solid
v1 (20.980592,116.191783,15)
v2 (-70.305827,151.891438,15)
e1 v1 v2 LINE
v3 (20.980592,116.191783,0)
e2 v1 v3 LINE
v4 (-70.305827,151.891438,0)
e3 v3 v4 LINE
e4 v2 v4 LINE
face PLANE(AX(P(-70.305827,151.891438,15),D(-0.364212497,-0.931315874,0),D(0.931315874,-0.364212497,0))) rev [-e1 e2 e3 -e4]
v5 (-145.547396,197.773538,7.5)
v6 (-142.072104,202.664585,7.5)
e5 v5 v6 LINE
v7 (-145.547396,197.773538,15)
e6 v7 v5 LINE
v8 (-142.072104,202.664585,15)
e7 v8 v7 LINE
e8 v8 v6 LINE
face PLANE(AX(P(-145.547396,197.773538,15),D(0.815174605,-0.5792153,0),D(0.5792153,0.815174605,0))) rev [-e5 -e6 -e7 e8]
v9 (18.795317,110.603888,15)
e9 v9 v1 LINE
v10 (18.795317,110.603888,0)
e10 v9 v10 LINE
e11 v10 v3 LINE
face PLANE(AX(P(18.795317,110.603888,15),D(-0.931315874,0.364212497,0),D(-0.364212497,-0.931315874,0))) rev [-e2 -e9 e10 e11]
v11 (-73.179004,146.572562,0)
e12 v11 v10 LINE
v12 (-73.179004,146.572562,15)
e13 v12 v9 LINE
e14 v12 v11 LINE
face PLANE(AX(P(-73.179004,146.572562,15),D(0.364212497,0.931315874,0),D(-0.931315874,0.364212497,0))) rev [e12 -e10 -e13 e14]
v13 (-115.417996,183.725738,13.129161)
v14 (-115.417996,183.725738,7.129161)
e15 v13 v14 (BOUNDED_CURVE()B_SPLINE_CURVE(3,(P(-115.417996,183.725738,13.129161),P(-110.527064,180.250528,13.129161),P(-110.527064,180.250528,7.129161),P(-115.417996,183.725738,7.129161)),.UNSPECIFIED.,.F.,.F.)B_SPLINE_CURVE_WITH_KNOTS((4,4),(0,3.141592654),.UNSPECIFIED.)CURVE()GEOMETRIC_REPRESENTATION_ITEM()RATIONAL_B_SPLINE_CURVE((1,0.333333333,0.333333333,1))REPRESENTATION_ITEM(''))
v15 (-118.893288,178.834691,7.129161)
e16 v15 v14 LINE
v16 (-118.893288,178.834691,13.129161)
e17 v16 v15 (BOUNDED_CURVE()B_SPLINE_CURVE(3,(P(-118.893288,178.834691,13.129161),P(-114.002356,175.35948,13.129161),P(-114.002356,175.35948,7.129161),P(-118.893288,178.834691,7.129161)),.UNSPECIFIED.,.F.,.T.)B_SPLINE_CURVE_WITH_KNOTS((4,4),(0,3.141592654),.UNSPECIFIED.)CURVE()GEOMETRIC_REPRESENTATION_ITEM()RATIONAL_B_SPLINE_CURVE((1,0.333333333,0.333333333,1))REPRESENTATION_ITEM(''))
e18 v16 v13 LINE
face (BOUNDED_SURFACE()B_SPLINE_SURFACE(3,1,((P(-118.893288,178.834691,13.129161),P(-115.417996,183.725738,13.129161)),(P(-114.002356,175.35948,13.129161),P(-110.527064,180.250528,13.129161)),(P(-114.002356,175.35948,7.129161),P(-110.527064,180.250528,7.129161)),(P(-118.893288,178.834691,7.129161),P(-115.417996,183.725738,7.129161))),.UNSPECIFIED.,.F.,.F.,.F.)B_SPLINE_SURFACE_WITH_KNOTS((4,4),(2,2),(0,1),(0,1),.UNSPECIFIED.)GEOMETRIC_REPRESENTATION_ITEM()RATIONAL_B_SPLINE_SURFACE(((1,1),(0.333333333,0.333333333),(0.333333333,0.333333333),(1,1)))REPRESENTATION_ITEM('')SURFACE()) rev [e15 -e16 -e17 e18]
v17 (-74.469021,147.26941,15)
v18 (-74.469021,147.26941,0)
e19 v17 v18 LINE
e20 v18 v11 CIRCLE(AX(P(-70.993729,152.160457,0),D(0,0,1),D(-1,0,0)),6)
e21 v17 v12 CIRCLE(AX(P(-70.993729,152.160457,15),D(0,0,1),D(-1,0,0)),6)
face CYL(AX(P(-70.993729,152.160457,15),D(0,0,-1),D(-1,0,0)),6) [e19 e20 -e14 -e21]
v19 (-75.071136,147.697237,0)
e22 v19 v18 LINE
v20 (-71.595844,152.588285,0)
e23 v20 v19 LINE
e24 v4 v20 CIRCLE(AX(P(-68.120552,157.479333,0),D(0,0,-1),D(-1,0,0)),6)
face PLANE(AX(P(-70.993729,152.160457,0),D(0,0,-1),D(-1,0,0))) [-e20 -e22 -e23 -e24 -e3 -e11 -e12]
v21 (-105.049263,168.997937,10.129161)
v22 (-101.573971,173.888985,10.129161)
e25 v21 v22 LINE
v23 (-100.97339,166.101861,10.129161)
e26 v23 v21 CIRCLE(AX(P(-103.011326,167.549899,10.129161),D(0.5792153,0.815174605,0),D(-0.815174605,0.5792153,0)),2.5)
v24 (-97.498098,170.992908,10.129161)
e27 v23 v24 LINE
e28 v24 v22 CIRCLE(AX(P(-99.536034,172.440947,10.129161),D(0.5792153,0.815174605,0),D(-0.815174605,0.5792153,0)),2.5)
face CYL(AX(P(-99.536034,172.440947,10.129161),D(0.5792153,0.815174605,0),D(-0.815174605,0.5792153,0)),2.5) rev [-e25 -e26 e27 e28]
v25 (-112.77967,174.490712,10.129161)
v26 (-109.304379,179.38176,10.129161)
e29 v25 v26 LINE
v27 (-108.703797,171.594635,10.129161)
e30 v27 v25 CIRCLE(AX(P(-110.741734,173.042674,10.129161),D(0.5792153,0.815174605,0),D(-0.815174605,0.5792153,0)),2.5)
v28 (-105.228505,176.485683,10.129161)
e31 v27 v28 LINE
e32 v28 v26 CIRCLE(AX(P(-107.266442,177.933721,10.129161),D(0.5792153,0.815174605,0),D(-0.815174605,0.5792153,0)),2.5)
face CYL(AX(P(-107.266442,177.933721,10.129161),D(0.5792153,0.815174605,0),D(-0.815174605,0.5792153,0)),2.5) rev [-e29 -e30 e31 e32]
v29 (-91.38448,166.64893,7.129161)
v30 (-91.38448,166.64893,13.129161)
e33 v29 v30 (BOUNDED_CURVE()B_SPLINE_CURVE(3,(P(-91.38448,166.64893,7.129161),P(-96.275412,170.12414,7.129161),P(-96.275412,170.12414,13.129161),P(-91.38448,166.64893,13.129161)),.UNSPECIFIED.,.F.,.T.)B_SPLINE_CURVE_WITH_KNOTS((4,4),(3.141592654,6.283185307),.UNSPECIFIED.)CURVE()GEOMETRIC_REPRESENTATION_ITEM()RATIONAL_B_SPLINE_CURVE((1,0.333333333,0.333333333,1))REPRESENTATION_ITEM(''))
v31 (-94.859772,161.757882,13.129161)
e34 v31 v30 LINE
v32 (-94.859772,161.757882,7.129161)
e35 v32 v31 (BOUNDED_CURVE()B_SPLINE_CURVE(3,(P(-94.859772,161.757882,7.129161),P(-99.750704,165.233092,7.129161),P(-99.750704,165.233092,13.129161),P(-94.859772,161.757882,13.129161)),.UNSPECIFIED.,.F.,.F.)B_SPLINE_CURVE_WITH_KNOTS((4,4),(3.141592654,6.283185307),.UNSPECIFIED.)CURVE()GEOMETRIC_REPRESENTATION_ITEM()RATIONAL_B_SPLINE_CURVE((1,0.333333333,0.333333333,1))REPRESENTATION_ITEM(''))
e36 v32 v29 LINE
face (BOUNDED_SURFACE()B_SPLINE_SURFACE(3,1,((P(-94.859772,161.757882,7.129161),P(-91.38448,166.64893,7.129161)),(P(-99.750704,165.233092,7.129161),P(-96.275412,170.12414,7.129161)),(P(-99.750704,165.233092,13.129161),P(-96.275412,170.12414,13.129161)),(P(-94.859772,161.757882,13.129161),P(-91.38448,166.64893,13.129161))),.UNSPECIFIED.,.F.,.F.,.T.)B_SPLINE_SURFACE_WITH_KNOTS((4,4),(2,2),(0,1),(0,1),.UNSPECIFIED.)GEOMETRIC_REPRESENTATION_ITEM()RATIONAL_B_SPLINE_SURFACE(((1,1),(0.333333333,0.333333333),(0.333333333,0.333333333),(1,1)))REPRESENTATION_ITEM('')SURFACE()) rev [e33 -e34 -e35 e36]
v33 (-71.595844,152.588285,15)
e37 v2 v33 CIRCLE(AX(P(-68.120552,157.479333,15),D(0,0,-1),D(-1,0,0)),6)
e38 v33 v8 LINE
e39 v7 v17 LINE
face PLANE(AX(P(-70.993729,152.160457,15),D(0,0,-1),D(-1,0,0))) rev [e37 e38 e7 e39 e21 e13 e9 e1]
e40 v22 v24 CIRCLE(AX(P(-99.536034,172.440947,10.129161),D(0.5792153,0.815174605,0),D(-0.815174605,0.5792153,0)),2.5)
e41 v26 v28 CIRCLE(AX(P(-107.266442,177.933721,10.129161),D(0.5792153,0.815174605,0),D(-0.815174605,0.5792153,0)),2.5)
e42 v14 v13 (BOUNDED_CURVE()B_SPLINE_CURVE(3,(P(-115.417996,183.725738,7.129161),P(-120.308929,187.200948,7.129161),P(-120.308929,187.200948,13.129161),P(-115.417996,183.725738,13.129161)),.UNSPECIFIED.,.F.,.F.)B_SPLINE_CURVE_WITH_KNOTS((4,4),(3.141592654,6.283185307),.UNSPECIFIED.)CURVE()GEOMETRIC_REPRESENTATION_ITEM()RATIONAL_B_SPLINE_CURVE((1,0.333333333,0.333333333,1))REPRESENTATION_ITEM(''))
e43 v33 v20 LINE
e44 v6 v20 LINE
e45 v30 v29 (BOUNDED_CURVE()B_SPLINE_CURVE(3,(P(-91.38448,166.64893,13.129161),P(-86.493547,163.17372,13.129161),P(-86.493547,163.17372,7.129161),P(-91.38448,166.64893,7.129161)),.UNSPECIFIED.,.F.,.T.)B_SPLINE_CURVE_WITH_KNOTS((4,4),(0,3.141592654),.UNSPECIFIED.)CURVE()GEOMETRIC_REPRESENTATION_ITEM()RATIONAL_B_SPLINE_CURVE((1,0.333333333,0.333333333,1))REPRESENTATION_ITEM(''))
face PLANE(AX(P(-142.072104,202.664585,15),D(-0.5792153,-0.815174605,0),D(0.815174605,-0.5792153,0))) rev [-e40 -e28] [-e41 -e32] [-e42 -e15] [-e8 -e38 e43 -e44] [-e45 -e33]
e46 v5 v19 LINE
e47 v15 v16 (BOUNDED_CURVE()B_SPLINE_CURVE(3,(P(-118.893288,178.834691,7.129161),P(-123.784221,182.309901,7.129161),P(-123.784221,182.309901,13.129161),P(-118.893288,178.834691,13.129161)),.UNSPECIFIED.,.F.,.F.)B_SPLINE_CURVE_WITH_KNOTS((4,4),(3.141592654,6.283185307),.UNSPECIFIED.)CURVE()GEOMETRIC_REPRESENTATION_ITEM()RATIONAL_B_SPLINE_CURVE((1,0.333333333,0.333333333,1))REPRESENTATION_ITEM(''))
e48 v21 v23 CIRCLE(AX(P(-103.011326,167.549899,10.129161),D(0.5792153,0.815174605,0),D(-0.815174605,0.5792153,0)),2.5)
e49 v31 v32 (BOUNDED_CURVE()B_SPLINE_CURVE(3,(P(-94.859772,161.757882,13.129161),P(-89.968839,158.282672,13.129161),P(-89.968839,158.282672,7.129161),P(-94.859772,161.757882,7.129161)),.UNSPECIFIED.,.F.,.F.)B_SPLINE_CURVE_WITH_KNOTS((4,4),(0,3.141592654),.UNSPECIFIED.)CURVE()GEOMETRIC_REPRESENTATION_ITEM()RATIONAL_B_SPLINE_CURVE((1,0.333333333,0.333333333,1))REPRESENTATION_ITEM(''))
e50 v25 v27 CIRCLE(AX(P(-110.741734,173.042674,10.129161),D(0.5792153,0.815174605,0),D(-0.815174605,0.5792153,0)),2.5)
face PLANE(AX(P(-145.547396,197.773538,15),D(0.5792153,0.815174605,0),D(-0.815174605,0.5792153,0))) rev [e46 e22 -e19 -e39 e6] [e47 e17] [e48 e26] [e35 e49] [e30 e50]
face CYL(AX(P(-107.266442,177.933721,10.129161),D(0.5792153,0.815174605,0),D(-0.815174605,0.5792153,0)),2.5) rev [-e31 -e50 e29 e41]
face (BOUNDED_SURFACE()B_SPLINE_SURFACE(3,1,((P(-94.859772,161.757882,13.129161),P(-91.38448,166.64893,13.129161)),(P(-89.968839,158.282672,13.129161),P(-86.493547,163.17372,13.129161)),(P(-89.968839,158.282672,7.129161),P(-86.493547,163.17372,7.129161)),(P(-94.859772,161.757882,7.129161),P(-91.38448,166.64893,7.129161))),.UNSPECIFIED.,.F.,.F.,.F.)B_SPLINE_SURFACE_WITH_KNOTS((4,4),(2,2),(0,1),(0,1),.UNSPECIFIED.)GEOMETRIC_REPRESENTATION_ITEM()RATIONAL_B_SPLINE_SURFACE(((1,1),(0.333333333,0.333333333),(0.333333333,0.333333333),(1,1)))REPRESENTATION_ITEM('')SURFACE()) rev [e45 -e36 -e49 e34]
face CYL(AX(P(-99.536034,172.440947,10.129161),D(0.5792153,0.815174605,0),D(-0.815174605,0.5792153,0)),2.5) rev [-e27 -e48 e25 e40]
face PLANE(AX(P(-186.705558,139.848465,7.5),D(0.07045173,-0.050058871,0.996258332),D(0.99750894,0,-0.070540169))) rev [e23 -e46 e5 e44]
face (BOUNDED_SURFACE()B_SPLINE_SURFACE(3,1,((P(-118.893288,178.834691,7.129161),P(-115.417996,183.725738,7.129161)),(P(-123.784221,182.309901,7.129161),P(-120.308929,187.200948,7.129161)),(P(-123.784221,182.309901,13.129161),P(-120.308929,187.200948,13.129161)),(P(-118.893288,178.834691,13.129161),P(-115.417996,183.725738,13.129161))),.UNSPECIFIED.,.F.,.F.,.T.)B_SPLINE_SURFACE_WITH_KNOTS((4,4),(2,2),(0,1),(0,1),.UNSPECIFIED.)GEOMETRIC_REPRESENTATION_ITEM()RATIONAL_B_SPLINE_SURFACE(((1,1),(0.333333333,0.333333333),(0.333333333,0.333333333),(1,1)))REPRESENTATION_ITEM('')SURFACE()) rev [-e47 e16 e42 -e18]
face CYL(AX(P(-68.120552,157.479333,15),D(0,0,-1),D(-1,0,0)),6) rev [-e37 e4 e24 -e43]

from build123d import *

# Parameters (mm, degrees)
EXTRUDE_1_DEPTH     = 15
CUT_EXTRUDE_1_DEPTH = 237.517683659
SKETCH_5_RX         = 3
SKETCH_5_RY         = 2.999929495
CUT_EXTRUDE_2_DEPTH = 237.517683659
HOLE_WIZARD_M6_1_D  = 5


with BuildPart() as part:
    # 草图1 → 凸台-拉伸1 (new body)
    with BuildSketch(Plane.XY):
        with BuildLine():
            Line((-145.547396155, 197.773537563), (-142.072104357, 202.664585193))
            Line((-142.072104357, 202.664585193), (-71.595844229, 152.588285115))
            ThreePointArc((-71.595844229, 152.588285115), (-70.97220164, 152.200308518), (-70.305827411, 151.891437501))
            Line((-70.305827411, 151.891437501), (20.980591756, 116.19178332))
            Line((20.980591756, 116.19178332), (18.795316776, 110.603888076))
            Line((18.795316776, 110.603888076), (-73.179003731, 146.5725619))
            ThreePointArc((-73.179003731, 146.5725619), (-73.84537796, 146.881432918), (-74.469020549, 147.269409515))
            Line((-74.469020549, 147.269409515), (-145.547396155, 197.773537563))
        make_face()
    extrude(amount=EXTRUDE_1_DEPTH)

    # 草图4 → 切除-拉伸1 (cut, through all)
    with BuildSketch(Plane(origin=(48.026613519, 67.591577297, 0), x_dir=(0.8151746049568697, -0.5792152997231785, 0), z_dir=(0.5792152997231785, 0.8151746049568697, 0))):
        Polygon((-233.2, -7.5), (-146.744583334, 0), (-233.2, 0), align=None)
    extrude(amount=-CUT_EXTRUDE_1_DEPTH, mode=Mode.SUBTRACT)

    # 草图5 → 切除-拉伸2 (cut, through all)
    with BuildSketch(Plane(origin=(48.026613519, 67.591577297, 0), x_dir=(0.8151746049568697, -0.5792152997231785, 0), z_dir=(0.5792152997231785, 0.8151746049568697, 0))):
        with Locations(Location((-171.01991706, -10.129161482), (0, 0, -90))):
            Ellipse(SKETCH_5_RX, SKETCH_5_RY)
        with Locations(Location((-200.50257822, -10.129161482), (0, 0, -90))):
            Ellipse(SKETCH_5_RX, SKETCH_5_RY)
    extrude(amount=-CUT_EXTRUDE_2_DEPTH, mode=Mode.SUBTRACT)

    # M6 螺纹孔1 (through all)
    with Locations(Plane(origin=(48.026613519, 67.591577297, 0), x_dir=(0.8151746049568697, -0.5792152997231785, 0), z_dir=(0.5792152997231785, 0.8151746049568697, 0))):
        with Locations((-181.019682042, -10.129161482), (-190.502813238, -10.129161482)):
            Hole(HOLE_WIZARD_M6_1_D / 2)


solid = part.part
